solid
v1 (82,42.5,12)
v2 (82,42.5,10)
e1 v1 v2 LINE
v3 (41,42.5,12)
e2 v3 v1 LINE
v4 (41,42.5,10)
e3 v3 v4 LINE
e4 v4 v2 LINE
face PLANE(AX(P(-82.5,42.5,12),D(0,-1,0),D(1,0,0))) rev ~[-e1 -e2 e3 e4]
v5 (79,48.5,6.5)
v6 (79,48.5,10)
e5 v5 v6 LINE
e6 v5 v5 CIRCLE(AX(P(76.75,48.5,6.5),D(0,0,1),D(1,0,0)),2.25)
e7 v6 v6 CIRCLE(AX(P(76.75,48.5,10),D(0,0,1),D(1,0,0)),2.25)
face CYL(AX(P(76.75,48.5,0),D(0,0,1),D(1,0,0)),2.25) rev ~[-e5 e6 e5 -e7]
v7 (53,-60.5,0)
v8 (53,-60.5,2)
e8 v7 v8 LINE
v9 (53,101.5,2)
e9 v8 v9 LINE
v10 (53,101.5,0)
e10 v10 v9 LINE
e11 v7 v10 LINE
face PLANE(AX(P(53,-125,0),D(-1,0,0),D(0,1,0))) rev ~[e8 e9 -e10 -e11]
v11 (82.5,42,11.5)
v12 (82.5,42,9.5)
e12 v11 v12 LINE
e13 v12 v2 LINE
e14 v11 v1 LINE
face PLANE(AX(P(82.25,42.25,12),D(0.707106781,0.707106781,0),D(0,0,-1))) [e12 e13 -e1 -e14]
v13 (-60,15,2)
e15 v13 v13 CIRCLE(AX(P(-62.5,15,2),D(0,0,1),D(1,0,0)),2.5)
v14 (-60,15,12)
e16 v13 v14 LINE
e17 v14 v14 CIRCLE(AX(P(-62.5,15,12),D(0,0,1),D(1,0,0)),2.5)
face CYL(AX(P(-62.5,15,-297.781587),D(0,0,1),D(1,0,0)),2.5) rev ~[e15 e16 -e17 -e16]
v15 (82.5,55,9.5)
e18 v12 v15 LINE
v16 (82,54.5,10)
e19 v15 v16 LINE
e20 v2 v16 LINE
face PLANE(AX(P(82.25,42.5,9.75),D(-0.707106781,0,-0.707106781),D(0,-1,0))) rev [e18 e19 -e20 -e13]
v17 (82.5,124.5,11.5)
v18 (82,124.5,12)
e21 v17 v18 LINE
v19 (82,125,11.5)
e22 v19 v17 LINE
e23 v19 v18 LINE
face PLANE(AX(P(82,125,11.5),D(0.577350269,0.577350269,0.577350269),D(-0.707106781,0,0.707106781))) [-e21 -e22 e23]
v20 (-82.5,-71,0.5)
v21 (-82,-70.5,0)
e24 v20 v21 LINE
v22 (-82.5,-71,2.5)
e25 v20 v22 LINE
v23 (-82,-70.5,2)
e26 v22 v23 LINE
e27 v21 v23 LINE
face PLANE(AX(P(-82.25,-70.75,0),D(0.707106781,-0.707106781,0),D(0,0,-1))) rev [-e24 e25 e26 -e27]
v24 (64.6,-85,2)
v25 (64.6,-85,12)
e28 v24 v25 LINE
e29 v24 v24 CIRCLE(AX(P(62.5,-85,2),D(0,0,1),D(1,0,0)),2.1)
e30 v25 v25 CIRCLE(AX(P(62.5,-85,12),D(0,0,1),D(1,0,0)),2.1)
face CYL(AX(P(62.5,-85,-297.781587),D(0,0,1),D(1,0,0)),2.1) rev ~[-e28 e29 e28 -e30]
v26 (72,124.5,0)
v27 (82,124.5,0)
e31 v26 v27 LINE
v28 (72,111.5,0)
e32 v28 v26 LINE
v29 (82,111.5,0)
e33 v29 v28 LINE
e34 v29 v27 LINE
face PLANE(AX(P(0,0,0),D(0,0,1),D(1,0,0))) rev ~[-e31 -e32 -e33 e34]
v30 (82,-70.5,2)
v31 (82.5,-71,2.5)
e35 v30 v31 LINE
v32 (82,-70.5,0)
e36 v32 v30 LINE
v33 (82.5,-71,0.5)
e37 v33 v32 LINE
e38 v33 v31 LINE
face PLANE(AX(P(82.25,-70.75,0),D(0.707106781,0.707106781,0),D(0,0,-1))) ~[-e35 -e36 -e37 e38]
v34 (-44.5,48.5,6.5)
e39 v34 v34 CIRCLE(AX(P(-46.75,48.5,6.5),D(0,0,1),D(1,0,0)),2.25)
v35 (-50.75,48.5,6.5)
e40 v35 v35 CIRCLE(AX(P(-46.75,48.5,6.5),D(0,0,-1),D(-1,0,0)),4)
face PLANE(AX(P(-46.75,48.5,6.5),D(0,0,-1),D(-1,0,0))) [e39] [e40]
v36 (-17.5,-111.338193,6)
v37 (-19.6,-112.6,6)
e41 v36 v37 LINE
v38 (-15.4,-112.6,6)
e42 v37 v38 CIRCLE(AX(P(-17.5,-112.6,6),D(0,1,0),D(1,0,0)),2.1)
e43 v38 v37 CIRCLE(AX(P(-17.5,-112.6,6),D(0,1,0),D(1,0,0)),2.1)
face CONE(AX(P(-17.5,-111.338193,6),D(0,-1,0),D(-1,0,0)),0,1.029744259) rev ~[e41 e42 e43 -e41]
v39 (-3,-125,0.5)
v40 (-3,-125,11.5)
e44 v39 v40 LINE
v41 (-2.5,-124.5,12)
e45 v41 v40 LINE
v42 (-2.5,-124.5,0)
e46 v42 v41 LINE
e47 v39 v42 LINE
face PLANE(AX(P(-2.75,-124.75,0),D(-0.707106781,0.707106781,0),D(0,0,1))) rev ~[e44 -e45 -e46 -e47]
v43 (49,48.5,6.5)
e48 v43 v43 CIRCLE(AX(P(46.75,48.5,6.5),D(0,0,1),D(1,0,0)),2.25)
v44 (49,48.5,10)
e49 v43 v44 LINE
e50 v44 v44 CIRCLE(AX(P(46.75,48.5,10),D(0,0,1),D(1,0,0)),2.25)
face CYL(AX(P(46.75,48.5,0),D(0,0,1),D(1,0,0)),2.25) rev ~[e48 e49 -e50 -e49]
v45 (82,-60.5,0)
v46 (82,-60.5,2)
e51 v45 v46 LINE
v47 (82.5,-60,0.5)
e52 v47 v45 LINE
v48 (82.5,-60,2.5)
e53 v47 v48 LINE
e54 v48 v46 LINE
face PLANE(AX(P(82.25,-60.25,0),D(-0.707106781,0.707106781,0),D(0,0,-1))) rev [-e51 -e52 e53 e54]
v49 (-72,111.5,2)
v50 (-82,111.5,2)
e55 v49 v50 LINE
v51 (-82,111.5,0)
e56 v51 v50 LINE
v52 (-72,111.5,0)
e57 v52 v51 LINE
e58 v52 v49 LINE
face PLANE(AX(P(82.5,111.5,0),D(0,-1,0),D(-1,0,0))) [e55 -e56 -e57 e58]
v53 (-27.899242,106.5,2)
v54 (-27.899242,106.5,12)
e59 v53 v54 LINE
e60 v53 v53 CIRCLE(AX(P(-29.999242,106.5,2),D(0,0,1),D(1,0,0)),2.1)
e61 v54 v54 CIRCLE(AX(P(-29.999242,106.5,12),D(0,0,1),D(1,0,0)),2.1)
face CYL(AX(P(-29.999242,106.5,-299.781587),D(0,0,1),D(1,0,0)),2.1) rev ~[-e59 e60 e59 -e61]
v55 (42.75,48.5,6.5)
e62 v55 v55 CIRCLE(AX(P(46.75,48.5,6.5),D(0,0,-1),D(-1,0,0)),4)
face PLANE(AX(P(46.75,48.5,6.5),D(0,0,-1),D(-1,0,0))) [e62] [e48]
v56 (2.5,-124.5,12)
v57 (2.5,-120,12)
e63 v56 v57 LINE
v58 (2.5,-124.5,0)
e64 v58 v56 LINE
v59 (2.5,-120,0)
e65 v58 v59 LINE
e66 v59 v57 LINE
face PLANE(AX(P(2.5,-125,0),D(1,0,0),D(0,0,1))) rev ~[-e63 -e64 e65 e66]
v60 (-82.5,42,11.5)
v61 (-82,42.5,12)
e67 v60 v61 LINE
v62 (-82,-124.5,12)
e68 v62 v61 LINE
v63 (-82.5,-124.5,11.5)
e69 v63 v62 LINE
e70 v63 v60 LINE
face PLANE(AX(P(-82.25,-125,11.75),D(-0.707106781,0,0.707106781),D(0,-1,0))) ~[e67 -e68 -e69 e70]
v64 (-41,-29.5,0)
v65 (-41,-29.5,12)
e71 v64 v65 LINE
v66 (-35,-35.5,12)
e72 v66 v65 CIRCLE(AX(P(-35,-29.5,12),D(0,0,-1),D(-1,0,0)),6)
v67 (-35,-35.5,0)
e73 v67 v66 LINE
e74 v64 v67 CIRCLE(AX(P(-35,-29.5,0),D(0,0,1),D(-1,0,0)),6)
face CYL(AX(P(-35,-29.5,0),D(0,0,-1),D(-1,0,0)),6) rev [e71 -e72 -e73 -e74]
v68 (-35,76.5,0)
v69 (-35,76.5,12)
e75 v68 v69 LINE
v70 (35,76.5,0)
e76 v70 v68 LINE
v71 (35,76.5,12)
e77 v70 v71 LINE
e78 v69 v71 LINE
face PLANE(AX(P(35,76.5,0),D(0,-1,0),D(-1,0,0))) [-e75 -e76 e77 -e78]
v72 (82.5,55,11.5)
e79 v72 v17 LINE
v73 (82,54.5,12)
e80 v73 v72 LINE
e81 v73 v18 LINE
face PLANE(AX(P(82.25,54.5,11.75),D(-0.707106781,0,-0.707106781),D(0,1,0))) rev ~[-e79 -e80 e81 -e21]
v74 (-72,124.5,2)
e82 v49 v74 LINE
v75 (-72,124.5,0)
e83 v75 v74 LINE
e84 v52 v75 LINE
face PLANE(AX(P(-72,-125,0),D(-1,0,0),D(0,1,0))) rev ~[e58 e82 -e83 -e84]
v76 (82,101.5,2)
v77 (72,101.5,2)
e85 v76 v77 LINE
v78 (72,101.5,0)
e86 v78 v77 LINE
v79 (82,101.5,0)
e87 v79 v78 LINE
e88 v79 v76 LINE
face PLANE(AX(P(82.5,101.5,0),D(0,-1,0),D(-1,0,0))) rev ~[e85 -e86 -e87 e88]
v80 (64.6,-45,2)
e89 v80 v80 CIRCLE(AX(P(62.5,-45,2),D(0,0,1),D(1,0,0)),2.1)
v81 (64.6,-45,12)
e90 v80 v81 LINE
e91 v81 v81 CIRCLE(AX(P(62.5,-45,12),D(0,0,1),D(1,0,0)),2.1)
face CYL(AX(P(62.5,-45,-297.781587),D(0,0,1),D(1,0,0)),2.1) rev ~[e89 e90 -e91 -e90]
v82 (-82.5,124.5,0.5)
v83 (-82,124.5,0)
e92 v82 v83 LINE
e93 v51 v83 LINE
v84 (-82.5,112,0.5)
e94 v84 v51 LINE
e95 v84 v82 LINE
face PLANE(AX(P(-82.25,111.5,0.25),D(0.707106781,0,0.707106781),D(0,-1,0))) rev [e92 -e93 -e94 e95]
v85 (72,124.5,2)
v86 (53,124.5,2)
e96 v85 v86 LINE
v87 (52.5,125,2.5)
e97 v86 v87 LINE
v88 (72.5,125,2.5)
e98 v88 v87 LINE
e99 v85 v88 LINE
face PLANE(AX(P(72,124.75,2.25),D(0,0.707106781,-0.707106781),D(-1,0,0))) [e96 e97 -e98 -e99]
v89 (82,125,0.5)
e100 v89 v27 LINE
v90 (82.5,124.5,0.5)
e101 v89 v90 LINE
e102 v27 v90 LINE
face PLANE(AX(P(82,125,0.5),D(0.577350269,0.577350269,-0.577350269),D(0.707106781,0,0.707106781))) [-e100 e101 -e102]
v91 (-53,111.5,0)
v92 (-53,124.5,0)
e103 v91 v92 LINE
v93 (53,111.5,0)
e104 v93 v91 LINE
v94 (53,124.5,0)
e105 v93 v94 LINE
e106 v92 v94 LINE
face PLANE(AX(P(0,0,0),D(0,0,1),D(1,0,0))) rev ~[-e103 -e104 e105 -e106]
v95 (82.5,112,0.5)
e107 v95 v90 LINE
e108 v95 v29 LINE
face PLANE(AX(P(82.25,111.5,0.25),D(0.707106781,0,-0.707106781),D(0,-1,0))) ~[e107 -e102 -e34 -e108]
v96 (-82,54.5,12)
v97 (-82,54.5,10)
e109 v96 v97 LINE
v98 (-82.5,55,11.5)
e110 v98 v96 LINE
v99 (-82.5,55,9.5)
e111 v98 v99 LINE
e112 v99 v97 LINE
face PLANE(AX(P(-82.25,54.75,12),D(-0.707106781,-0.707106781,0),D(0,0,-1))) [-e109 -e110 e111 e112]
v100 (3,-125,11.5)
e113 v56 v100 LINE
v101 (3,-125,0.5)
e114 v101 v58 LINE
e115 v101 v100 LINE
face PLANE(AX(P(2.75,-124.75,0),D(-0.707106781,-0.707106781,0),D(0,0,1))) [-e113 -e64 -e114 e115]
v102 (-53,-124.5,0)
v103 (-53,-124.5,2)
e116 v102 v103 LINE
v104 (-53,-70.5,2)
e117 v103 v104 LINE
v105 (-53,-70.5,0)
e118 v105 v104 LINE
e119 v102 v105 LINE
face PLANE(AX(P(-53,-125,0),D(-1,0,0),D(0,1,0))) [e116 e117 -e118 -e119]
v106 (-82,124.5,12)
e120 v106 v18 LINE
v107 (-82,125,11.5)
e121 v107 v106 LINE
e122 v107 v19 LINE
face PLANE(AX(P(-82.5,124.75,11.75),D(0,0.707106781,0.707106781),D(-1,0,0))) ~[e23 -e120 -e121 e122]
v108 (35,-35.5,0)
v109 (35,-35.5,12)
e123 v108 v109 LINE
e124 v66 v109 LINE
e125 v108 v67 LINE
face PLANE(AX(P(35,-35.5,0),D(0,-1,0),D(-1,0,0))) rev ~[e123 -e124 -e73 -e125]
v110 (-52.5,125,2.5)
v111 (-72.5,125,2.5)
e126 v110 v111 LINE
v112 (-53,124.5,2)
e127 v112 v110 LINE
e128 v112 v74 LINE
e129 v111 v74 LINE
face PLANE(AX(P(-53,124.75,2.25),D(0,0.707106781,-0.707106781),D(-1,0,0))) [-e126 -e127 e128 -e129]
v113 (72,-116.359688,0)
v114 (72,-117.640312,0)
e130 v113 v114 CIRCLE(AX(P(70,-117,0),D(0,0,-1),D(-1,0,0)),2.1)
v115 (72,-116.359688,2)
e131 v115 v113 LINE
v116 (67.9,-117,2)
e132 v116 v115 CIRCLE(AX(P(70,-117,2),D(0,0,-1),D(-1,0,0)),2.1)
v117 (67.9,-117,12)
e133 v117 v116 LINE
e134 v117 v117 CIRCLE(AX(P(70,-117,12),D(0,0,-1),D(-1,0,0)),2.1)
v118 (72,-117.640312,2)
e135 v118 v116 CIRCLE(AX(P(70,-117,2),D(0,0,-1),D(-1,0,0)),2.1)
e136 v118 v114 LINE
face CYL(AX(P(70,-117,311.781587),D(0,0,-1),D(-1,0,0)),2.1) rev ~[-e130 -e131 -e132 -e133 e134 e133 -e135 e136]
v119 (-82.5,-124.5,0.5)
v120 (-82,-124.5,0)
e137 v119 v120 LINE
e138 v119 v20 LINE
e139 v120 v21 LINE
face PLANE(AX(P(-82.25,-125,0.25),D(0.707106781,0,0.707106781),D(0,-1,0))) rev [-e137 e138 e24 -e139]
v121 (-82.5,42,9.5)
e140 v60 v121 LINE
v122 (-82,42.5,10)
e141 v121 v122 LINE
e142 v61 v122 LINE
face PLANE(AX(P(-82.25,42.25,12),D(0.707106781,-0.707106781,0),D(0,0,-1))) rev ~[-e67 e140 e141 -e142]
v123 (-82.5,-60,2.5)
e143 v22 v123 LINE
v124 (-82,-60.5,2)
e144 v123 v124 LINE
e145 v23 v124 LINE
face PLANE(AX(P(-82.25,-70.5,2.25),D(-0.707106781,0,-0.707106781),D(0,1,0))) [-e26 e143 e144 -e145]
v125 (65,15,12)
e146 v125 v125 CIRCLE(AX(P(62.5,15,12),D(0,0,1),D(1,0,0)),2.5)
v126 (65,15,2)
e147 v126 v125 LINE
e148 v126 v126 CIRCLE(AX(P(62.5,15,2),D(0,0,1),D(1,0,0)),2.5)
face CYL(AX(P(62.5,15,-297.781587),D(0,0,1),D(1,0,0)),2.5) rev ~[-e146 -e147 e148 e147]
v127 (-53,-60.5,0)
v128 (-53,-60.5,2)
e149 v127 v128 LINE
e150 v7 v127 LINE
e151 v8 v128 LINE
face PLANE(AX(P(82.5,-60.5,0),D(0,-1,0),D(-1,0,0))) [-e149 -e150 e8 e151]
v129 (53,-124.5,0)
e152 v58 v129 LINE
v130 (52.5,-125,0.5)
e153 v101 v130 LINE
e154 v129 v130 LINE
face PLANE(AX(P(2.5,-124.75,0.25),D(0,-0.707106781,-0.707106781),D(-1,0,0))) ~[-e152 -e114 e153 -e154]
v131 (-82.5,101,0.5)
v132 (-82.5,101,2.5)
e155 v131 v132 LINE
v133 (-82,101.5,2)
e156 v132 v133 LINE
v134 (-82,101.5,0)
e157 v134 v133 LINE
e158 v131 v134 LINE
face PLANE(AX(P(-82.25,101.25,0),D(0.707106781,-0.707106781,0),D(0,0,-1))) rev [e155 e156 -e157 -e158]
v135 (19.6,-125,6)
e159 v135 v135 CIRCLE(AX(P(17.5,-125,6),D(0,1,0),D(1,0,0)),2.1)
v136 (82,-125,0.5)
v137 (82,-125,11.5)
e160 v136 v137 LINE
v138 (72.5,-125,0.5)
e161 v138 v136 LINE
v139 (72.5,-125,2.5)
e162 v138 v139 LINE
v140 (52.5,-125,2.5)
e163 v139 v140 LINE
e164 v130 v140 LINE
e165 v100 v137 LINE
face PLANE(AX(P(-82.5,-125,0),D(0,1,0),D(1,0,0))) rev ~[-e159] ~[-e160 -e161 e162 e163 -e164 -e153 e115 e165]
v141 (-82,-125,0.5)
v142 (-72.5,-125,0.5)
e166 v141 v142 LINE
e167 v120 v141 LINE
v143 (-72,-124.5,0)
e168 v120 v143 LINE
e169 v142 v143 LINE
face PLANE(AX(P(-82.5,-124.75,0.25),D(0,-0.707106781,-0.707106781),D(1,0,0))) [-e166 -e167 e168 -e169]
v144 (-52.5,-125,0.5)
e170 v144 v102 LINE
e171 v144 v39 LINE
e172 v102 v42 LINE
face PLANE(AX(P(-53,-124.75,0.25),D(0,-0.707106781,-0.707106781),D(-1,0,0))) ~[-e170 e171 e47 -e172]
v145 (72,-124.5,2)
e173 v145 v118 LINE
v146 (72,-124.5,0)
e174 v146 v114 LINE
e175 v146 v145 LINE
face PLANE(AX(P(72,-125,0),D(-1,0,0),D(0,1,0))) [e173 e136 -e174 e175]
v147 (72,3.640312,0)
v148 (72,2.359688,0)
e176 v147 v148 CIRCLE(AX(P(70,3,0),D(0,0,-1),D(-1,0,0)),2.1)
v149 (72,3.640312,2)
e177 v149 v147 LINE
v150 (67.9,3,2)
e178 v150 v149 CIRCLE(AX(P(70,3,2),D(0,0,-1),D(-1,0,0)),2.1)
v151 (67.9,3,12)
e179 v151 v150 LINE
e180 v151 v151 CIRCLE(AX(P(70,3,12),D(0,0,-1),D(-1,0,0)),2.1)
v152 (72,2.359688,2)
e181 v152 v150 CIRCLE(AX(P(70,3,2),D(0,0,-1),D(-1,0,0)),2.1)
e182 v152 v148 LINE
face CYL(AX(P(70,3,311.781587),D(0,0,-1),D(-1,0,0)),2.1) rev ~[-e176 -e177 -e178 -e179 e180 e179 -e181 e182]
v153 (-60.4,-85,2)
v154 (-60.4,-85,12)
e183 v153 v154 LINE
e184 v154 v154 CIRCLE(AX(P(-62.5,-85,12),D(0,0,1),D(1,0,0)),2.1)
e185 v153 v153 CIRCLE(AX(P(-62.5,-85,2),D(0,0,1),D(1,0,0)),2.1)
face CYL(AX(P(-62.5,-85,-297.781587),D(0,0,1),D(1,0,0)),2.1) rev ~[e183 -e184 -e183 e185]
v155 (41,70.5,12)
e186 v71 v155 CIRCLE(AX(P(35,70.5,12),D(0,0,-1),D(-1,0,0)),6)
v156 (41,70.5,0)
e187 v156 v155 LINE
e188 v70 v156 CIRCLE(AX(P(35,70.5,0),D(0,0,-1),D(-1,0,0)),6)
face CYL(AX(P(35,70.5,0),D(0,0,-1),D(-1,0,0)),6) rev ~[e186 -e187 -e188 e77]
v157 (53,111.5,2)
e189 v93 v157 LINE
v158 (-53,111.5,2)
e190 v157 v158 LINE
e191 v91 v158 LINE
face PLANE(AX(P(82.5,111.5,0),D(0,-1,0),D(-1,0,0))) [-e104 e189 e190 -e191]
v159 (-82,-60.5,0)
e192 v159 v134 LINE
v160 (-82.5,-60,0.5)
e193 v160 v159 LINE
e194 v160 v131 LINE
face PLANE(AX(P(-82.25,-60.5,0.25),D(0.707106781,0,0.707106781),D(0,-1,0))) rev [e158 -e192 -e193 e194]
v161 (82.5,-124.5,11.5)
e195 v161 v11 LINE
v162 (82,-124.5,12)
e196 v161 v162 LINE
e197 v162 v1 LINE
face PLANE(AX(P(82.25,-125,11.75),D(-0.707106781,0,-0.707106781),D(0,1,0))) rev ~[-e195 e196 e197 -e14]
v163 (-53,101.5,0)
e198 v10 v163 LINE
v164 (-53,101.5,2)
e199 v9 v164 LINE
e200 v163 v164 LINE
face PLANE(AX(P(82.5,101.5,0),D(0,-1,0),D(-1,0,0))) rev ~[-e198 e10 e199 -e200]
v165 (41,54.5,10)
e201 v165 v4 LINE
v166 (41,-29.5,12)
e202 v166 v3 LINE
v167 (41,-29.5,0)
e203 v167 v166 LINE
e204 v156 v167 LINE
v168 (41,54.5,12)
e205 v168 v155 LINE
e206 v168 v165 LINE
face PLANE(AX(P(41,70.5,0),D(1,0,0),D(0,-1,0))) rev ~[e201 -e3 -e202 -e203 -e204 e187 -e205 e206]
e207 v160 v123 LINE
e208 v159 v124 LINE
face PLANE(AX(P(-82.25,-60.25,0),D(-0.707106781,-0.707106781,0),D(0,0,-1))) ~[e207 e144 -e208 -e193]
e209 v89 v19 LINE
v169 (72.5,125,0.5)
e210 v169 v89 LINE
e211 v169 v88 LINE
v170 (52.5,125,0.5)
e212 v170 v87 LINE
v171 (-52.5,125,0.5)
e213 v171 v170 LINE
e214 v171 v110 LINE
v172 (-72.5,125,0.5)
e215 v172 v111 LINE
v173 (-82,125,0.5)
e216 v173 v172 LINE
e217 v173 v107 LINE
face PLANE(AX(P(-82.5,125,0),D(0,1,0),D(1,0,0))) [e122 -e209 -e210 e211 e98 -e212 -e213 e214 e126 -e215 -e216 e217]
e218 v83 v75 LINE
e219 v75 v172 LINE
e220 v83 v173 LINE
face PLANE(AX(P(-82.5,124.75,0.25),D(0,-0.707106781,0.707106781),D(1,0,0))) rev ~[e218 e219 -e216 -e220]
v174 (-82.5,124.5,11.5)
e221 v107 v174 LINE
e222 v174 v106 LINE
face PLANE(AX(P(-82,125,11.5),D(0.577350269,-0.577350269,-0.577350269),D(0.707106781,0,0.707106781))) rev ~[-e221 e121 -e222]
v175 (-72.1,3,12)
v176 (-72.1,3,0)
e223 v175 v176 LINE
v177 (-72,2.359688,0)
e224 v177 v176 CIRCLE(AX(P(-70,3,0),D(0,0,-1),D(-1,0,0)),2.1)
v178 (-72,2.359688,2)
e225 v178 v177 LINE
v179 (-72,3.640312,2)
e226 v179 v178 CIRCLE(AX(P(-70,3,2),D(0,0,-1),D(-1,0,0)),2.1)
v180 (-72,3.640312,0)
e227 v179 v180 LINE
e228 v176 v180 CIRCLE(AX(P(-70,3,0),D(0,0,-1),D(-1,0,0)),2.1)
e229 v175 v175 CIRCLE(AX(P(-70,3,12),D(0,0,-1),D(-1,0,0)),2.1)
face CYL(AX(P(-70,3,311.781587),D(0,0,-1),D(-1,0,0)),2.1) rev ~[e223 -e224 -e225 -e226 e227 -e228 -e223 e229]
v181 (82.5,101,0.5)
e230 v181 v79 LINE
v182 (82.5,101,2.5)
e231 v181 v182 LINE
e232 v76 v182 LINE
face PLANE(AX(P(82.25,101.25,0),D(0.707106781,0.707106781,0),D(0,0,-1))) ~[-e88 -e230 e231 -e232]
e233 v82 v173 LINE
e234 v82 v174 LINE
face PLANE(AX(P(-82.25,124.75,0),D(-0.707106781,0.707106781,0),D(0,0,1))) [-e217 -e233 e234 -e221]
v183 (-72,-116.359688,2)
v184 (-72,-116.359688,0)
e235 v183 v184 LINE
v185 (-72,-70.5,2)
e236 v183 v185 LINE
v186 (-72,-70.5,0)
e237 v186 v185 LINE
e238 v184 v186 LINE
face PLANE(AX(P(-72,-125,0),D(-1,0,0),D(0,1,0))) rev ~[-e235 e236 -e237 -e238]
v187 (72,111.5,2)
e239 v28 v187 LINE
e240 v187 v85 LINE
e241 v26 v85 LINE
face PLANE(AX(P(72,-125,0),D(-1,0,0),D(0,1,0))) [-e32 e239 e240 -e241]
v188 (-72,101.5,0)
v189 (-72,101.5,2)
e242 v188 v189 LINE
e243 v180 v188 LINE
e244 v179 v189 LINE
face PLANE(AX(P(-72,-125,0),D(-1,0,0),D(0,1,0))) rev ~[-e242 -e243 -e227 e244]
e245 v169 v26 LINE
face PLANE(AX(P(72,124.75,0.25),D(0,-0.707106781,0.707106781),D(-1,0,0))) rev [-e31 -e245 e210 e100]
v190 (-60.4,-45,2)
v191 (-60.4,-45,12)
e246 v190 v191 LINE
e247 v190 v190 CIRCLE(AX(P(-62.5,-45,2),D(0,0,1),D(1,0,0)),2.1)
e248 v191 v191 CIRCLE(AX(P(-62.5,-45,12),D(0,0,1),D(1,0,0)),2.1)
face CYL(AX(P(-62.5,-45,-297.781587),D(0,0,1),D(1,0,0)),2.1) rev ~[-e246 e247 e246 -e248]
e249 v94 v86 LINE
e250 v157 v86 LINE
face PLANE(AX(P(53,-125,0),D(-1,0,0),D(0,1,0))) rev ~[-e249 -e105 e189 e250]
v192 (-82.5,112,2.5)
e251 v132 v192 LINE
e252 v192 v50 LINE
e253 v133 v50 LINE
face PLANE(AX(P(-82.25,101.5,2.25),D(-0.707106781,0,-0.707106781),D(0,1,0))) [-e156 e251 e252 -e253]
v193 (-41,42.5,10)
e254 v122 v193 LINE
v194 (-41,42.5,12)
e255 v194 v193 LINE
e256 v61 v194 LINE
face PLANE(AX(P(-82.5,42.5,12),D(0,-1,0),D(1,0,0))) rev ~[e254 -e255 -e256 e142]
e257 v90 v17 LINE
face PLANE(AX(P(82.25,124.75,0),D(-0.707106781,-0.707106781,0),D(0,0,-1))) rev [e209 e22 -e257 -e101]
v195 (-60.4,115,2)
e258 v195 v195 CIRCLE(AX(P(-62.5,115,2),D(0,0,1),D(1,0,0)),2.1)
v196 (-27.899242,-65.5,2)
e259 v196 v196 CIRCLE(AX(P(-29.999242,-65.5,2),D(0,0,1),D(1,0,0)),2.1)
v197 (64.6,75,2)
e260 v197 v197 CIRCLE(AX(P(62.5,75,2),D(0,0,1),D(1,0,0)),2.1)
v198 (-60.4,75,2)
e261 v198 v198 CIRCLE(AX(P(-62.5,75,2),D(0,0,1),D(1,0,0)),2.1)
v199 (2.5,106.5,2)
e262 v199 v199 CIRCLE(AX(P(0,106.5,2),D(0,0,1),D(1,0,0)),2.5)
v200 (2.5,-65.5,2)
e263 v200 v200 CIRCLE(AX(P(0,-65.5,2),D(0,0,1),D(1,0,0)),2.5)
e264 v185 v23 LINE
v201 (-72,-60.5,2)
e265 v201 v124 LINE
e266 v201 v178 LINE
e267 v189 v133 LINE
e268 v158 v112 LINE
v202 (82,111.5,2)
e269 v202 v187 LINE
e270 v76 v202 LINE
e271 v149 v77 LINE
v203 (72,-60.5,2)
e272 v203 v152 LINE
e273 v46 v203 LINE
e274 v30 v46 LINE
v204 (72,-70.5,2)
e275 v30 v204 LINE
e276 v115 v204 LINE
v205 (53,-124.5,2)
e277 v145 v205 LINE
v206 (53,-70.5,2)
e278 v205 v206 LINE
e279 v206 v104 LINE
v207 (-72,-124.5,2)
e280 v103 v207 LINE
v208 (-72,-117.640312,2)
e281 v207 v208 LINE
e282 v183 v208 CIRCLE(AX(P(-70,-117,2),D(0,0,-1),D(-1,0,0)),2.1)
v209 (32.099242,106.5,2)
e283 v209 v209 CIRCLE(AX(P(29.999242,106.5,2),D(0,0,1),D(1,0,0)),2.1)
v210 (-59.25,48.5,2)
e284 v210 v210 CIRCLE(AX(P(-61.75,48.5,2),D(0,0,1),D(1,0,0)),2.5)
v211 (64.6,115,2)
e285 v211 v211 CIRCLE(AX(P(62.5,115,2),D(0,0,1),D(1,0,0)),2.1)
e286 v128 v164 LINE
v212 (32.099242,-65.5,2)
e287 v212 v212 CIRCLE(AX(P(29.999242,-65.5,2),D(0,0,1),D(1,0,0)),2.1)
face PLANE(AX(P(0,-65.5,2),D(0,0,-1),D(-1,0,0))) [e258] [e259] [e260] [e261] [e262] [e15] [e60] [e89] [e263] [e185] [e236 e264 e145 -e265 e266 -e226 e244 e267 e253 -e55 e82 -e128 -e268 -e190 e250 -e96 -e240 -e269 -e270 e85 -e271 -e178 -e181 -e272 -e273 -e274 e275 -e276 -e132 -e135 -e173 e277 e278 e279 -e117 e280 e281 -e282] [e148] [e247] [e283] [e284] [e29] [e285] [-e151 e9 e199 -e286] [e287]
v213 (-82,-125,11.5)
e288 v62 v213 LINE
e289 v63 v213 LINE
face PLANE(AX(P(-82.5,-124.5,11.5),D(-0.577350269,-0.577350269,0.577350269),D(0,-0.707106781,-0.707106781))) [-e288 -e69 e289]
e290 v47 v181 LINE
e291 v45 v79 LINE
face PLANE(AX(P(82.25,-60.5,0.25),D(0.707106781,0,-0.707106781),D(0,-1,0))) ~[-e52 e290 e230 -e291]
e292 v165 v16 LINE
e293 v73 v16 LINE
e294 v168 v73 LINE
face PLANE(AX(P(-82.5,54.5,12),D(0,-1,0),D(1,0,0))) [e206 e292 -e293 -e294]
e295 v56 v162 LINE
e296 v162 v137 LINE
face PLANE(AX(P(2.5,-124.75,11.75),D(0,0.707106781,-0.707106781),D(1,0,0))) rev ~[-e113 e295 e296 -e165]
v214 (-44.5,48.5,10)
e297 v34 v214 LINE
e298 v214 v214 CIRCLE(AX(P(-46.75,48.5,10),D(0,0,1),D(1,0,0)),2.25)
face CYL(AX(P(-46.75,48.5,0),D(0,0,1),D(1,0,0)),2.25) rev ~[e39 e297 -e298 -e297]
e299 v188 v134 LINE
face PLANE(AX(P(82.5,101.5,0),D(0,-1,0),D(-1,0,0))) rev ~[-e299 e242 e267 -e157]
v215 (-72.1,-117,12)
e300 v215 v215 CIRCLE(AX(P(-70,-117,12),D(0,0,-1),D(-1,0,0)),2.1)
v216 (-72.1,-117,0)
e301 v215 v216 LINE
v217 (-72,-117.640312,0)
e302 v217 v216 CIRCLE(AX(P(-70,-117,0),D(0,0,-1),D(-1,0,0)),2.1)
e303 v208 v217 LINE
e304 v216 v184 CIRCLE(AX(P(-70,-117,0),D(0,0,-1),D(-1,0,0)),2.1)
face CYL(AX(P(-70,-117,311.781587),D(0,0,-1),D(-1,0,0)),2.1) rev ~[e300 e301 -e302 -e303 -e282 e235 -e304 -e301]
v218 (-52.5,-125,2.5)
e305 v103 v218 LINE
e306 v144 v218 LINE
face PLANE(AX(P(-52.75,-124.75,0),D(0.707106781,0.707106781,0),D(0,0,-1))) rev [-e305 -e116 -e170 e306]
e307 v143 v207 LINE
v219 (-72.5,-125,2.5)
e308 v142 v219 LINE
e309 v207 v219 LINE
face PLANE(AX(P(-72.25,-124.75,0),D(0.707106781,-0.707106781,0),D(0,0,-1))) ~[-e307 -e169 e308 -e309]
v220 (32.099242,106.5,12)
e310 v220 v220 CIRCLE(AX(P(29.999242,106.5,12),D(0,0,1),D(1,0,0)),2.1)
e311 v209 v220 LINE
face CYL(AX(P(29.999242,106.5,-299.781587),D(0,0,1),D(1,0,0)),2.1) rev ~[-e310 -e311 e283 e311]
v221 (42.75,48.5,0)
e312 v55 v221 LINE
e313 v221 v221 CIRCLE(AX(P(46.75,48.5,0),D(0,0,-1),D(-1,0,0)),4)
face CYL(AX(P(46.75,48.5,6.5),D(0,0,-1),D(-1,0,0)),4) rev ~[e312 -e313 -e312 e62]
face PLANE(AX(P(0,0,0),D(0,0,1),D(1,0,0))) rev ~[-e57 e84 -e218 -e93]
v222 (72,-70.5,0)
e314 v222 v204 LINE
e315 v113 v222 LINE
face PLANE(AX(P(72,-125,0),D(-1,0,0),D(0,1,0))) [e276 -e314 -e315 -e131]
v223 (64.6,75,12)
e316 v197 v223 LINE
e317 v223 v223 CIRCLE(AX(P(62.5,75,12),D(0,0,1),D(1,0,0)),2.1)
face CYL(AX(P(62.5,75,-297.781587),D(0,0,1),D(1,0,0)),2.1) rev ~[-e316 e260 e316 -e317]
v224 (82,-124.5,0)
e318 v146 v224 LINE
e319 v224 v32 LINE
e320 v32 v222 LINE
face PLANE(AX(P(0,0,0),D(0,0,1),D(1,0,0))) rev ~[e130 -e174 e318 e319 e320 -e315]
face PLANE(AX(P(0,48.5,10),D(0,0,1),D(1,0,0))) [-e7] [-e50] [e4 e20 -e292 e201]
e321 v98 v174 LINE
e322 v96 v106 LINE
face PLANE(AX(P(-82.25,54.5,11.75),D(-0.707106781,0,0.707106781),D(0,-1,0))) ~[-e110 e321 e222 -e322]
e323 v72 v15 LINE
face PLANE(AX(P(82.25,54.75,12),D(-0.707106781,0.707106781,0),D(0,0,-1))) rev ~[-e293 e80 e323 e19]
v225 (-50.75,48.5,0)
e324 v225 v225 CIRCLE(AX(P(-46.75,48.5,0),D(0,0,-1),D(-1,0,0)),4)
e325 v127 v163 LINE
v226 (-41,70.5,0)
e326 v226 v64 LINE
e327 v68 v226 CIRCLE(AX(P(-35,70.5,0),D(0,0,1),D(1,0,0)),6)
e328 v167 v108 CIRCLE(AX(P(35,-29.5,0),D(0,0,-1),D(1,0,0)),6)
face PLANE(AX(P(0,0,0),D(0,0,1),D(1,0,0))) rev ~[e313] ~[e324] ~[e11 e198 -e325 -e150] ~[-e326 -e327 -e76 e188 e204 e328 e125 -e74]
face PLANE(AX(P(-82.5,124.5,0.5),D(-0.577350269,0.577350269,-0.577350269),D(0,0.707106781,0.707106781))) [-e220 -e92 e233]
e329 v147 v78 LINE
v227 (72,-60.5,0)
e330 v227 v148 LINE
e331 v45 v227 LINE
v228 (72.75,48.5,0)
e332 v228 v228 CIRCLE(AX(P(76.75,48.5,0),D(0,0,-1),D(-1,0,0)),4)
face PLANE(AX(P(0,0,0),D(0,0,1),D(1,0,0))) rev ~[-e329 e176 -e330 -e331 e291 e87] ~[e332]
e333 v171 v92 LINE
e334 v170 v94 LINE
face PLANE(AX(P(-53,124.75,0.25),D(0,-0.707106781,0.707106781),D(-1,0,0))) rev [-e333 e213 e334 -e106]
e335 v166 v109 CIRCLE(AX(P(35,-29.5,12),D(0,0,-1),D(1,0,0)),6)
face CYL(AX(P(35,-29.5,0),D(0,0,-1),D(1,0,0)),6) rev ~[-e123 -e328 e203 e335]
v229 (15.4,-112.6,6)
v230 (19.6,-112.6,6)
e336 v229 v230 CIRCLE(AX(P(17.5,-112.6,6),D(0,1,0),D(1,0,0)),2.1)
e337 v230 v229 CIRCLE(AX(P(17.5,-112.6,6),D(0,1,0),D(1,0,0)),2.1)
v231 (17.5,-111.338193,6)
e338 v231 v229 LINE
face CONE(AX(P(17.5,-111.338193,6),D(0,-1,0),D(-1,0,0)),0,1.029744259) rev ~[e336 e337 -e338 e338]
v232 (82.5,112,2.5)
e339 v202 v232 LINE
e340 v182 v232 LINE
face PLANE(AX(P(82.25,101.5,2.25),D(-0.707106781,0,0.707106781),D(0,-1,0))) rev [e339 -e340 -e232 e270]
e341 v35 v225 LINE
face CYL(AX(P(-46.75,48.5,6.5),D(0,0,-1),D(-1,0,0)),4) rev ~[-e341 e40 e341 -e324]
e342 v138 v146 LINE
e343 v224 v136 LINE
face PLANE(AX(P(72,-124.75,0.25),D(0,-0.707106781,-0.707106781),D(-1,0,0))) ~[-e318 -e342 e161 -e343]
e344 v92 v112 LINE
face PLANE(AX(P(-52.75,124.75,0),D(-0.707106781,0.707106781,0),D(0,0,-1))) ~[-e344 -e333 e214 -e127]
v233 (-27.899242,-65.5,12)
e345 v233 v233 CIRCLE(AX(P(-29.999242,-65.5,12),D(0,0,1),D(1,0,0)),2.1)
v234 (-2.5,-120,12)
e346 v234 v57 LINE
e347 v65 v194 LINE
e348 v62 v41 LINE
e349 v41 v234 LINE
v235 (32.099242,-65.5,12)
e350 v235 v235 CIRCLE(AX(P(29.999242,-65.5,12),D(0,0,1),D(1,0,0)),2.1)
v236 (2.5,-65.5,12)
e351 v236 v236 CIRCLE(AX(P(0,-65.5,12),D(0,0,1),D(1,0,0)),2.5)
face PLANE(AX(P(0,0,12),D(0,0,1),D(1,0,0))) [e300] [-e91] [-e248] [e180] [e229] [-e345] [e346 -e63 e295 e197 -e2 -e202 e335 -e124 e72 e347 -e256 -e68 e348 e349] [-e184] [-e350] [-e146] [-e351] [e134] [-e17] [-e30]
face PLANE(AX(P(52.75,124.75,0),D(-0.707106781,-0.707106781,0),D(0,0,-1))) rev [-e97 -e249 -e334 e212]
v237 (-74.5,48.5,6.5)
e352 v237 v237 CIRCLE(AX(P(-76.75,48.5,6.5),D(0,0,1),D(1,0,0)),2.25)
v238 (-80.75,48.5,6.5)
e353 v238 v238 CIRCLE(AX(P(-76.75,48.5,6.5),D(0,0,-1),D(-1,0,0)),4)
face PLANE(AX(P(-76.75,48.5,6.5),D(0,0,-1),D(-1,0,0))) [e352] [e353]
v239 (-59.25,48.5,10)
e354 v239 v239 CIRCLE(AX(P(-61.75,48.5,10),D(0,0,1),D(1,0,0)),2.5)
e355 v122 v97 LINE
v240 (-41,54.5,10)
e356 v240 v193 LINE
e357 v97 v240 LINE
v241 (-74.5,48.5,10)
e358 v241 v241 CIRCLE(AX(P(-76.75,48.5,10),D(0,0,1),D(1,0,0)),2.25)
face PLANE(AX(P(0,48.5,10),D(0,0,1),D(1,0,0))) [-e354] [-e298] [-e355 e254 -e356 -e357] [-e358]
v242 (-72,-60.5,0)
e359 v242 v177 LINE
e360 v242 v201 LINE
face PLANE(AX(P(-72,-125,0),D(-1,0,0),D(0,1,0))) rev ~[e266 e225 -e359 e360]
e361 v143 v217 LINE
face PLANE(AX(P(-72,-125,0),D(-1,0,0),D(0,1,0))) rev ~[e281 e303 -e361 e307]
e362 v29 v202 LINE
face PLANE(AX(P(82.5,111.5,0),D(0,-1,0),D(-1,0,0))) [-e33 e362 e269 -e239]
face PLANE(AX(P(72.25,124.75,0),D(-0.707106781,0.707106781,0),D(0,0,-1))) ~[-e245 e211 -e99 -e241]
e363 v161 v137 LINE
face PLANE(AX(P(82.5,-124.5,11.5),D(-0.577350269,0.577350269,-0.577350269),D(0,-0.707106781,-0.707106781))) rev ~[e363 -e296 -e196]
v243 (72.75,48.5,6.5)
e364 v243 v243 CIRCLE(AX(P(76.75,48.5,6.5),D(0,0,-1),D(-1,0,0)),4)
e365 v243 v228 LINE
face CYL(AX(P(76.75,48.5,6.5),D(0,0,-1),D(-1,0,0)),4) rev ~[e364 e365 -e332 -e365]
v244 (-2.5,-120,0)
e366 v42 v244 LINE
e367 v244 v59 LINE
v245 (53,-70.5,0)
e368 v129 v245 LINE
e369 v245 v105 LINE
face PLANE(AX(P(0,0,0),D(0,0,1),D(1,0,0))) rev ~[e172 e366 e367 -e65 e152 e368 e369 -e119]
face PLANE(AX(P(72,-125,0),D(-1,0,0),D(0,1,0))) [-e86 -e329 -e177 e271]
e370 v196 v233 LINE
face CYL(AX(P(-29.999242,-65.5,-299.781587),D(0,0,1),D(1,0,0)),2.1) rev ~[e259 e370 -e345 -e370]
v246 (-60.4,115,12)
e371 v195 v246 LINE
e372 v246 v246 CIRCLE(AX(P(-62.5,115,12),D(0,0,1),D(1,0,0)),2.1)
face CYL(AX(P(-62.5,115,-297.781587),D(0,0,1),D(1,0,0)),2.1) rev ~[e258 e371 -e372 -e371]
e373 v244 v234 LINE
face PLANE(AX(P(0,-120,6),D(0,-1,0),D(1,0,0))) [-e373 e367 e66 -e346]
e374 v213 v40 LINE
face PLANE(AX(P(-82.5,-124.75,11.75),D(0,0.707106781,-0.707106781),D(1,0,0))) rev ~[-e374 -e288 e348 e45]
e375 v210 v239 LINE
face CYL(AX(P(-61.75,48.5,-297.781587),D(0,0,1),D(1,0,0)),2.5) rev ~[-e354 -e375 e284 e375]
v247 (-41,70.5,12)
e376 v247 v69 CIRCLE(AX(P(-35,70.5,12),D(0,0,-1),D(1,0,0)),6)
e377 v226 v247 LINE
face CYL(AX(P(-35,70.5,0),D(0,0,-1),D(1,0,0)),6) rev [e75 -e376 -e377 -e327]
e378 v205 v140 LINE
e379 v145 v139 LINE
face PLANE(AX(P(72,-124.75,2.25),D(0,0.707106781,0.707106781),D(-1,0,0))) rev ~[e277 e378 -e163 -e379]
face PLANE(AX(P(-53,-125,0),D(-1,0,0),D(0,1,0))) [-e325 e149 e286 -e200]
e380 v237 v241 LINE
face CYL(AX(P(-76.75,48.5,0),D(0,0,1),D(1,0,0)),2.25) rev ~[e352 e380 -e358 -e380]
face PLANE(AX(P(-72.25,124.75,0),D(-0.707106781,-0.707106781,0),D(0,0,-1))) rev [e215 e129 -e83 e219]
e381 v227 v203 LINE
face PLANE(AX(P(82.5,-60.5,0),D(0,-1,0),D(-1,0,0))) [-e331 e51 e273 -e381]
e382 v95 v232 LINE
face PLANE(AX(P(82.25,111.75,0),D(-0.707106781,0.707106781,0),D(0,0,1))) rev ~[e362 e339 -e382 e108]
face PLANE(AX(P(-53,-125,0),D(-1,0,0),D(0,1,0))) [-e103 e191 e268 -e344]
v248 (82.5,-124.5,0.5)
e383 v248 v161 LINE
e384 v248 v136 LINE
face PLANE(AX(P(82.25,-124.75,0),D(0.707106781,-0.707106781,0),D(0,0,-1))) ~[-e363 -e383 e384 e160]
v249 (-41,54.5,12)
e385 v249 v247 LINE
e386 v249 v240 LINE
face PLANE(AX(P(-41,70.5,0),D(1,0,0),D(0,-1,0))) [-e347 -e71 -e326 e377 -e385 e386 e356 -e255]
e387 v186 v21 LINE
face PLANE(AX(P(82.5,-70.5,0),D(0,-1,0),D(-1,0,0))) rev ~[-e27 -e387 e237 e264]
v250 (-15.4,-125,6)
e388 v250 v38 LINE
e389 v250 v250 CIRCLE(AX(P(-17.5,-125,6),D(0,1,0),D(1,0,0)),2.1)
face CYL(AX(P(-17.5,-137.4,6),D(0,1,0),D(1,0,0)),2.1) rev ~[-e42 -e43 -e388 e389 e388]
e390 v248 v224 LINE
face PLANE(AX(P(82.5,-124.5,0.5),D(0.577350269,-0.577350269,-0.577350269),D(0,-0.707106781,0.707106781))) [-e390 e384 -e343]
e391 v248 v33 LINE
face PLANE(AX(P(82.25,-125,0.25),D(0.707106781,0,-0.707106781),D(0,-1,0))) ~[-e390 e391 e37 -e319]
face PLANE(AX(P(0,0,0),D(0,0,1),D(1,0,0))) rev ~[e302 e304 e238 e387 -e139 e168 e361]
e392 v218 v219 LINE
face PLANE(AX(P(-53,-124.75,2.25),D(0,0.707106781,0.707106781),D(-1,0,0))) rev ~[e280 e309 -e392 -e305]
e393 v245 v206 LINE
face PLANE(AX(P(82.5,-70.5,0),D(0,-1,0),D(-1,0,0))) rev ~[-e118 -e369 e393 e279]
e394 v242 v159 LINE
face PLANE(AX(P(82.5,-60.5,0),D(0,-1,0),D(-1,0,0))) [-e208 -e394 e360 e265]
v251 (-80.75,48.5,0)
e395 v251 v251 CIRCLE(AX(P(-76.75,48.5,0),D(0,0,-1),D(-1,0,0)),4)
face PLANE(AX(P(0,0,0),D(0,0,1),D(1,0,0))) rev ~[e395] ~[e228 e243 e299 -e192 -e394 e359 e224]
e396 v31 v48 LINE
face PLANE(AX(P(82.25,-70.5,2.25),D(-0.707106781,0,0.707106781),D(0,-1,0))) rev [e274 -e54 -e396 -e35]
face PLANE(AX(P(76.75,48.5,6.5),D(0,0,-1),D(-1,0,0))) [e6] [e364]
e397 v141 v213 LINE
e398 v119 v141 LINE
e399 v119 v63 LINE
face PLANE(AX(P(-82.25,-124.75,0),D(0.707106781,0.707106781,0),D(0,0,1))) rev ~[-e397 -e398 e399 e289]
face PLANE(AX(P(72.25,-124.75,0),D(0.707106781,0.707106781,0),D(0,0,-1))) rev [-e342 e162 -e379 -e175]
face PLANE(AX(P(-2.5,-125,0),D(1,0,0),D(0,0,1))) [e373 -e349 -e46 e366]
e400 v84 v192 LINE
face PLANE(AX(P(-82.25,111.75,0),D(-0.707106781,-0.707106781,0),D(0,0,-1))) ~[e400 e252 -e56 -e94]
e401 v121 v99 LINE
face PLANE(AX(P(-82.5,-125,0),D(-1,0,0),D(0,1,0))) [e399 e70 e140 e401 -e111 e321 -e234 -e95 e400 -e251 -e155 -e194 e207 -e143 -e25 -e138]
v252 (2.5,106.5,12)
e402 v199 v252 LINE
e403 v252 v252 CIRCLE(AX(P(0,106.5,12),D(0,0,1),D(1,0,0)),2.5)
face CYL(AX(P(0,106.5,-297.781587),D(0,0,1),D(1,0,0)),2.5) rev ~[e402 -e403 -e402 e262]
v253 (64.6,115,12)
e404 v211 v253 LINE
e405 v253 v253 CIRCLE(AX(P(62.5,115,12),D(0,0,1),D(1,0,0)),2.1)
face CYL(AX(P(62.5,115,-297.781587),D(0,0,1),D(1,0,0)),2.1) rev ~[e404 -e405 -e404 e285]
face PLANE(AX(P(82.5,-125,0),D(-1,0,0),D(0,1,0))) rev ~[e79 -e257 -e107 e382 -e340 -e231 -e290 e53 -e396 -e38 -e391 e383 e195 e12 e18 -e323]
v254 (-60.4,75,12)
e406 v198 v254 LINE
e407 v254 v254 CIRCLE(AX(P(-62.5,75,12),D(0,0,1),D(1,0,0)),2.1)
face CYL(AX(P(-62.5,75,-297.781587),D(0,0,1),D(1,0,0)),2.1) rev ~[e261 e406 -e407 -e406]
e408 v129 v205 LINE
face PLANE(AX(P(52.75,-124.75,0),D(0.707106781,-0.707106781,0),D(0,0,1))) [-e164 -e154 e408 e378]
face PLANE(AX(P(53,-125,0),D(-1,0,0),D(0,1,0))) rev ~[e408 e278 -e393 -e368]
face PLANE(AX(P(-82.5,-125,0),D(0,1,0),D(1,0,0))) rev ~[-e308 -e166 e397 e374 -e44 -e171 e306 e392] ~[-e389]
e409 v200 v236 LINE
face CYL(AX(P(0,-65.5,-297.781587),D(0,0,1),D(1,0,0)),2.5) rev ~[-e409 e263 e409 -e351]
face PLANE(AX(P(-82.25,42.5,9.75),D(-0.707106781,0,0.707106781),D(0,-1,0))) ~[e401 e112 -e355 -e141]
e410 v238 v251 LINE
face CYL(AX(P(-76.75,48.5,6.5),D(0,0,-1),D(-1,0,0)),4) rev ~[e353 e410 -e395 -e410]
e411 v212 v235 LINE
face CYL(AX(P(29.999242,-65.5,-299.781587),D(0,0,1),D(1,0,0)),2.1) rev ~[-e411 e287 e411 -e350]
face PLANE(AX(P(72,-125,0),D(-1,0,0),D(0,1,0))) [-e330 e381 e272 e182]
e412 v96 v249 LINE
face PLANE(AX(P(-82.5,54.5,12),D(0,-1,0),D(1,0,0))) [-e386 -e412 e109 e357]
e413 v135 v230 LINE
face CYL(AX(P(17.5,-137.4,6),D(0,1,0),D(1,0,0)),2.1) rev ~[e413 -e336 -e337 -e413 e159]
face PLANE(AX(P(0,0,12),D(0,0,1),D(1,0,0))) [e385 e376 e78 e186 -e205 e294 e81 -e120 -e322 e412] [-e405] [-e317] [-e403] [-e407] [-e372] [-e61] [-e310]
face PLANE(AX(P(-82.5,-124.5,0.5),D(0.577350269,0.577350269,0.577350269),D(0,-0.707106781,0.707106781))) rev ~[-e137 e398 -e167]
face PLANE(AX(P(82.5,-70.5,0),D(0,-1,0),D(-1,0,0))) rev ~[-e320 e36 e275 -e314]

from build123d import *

# Parameters (mm, degrees)
SKETCH_1_W                   = 165
SKETCH_1_H                   = 250
EXTRUDE_1_DEPTH              = 12
SKETCH_2_W                   = 19
SKETCH_2_H                   = 250
CUT_EXTRUDE_1_DEPTH          = 2
SKETCH_3_W                   = 165
SKETCH_3_H                   = 10
CUT_EXTRUDE_2_DEPTH          = 2
SKETCH_4_W                   = 165
SKETCH_4_H                   = 10
CUT_EXTRUDE_3_DEPTH          = 2
HOLE_WIZARD_M5_1_D           = 4.2
MM_1_D                       = 5
CUT_EXTRUDE_4_DEPTH          = 151.250623959
SKETCH_11_W                  = 70
SKETCH_11_H                  = 112
CUT_EXTRUDE_5_DEPTH          = 151.250623959
SKETCH_13_W                  = 165
SKETCH_13_H                  = 12
CUT_EXTRUDE_6_DEPTH          = 2
HOLE_WIZARD_M5_2_D           = 4.2
HOLE_WIZARD_M4_1_D           = 4.5
HOLE_WIZARD_M4_1_CBORE_D     = 8
HOLE_WIZARD_M4_1_CBORE_DEPTH = 6.5
MM_2_D                       = 5
HOLE_WIZARD_M5_3_D           = 4.2
HOLE_WIZARD_M5_3_DEPTH       = 12.4
HOLE_WIZARD_M5_3_TIP         = 1.2618073
SKETCH_22_W                  = 5
SKETCH_22_H                  = 12
CUT_EXTRUDE_7_DEPTH          = 5
HOLE_WIZARD_M5_4_D           = 4.2
MM_3_D                       = 5
CHAMFER_1_SIZE               = 0.5


with BuildPart() as part:
    # 草图1 → 凸台-拉伸1 (new body)
    with BuildSketch(Plane.XY):
        Rectangle(SKETCH_1_W, SKETCH_1_H)
    extrude(amount=EXTRUDE_1_DEPTH)

    # 草图2 → 切除-拉伸1 (cut)
    with BuildSketch(Plane(origin=(0, 0, 0), x_dir=(-1, 0, 0), z_dir=(0, 0, -1))):
        with Locations((62.5, 0)):
            Rectangle(SKETCH_2_W, SKETCH_2_H)
        with Locations((-62.5, 0)):
            Rectangle(SKETCH_2_W, SKETCH_2_H)
    extrude(amount=-CUT_EXTRUDE_1_DEPTH, mode=Mode.SUBTRACT)

    # 草图3 → 切除-拉伸2 (cut)
    with BuildSketch(Plane(origin=(0, 0, 0), x_dir=(-1, 0, 0), z_dir=(0, 0, -1))):
        with Locations((0, -65.5)):
            Rectangle(SKETCH_3_W, SKETCH_3_H)
    extrude(amount=-CUT_EXTRUDE_2_DEPTH, mode=Mode.SUBTRACT)

    # 草图4 → 切除-拉伸3 (cut)
    with BuildSketch(Plane(origin=(0, 0, 0), x_dir=(-1, 0, 0), z_dir=(0, 0, -1))):
        with Locations((0, 106.5)):
            Rectangle(SKETCH_4_W, SKETCH_4_H)
    extrude(amount=-CUT_EXTRUDE_3_DEPTH, mode=Mode.SUBTRACT)

    # M5 螺纹孔1 (through all)
    with Locations(Plane(origin=(0, 0, 0), x_dir=(-1, 0, 0), z_dir=(0, 0, -1))):
        with Locations((-29.999242405, -65.5), (29.999242405, -65.5), (29.999242405, 106.5), (-29.999242405, 106.5)):
            Hole(HOLE_WIZARD_M5_1_D / 2)

    # 大小mm 暗销孔1 (through all)
    with Locations(Plane(origin=(0, 0, 2), x_dir=(-1, 0, 0), z_dir=(0, 0, -1))):
        with Locations((0, -65.5), (0, 106.5)):
            Hole(MM_1_D / 2)

    # 草图10 → 切除-拉伸4 (cut, through all)
    with BuildSketch(Plane(origin=(0, 0, 0), x_dir=(-1, 0, 0), z_dir=(0, 0, -1))):
        with BuildLine():
            Line((29, -29.5), (29, 70.5))
            ThreePointArc((29, 70.5), (35, 76.5), (41, 70.5))
            Line((41, 70.5), (41, -29.5))
            ThreePointArc((41, -29.5), (35, -35.5), (29, -29.5))
        make_face()
        with BuildLine():
            Line((-29, -29.5), (-29, 70.5))
            ThreePointArc((-29, 70.5), (-35, 76.5), (-41, 70.5))
            Line((-41, 70.5), (-41, -29.5))
            ThreePointArc((-41, -29.5), (-35, -35.5), (-29, -29.5))
        make_face()
    extrude(amount=-CUT_EXTRUDE_4_DEPTH, mode=Mode.SUBTRACT)

    # 草图11 → 切除-拉伸5 (cut, through all)
    with BuildSketch(Plane(origin=(0, 0, 0), x_dir=(-1, 0, 0), z_dir=(0, 0, -1))):
        with Locations((0, 20.5)):
            Rectangle(SKETCH_11_W, SKETCH_11_H)
    extrude(amount=-CUT_EXTRUDE_5_DEPTH, mode=Mode.SUBTRACT)

    # 草图13 → 切除-拉伸6 (cut)
    with BuildSketch(Plane.XY.offset(12)):
        with Locations((0, 48.5)):
            Rectangle(SKETCH_13_W, SKETCH_13_H)
    extrude(amount=-CUT_EXTRUDE_6_DEPTH, mode=Mode.SUBTRACT)

    # M5 螺纹孔2 (through all)
    with Locations(Plane.XY.offset(12)):
        with Locations((-70, 3), (-70, -117), (70, 3), (70, -117)):
            Hole(HOLE_WIZARD_M5_2_D / 2)

    # M4 六角凹头螺钉的柱形沉头孔1 (through all)
    with Locations(Plane(origin=(0, 0, 0), x_dir=(-1, 0, 0), z_dir=(0, 0, -1))):
        with Locations((46.75, 48.5), (76.75, 48.5), (-76.75, 48.5), (-46.75, 48.5)):
            CounterBoreHole(HOLE_WIZARD_M4_1_D / 2, HOLE_WIZARD_M4_1_CBORE_D / 2, HOLE_WIZARD_M4_1_CBORE_DEPTH)

    # 大小mm 暗销孔2 (through all)
    with Locations(Plane(origin=(0, 0, 2), x_dir=(-1, 0, 0), z_dir=(0, 0, -1))):
        with Locations((61.75, 48.5)):
            Hole(MM_2_D / 2)

    # M5 螺纹孔3
    with Locations(Plane(origin=(0, -125, 0), x_dir=(-1, 0, 0), z_dir=(0, -1, 0))):
        with Locations((-17.5, -6), (17.5, -6)):
            Hole(HOLE_WIZARD_M5_3_D / 2, depth=HOLE_WIZARD_M5_3_DEPTH)
            with Locations((0, 0, -(HOLE_WIZARD_M5_3_DEPTH + HOLE_WIZARD_M5_3_TIP / 2))):  # 118° drill point
                Cone(0, HOLE_WIZARD_M5_3_D / 2, HOLE_WIZARD_M5_3_TIP, mode=Mode.SUBTRACT)

    # 草图22 → 切除-拉伸7 (cut)
    with BuildSketch(Plane.XZ.offset(125)):
        with Locations((0, 6)):
            Rectangle(SKETCH_22_W, SKETCH_22_H)
    extrude(amount=-CUT_EXTRUDE_7_DEPTH, mode=Mode.SUBTRACT)

    # M5 螺纹孔4 (through all)
    with Locations(Plane(origin=(0, 0, 2), x_dir=(-1, 0, 0), z_dir=(0, 0, -1))):
        with Locations((62.5, -85), (62.5, -45), (62.5, 75), (62.5, 115), (-62.5, 115), (-62.5, 75), (-62.5, -45), (-62.5, -85)):
            Hole(HOLE_WIZARD_M5_4_D / 2)

    # 大小mm 暗销孔3 (through all)
    with Locations(Plane(origin=(0, 0, 2), x_dir=(-1, 0, 0), z_dir=(0, 0, -1))):
        with Locations((62.5, 15), (-62.5, 15)):
            Hole(MM_3_D / 2)

    # 倒角1
    chamfer_1_edges = [part.edges().sort_by_distance(p)[0] for p in [
        (82.5, 118.25, 0),
        (-82.5, 20.5, 0),
        (82.5, 111.5, 1),
        (-82.5, 101.5, 1),
        (82.5, 106.5, 2),
        (82.5, 101.5, 1),
        (-82.5, 106.5, 2),
        (-82.5, 111.5, 1),
        (-82.5, 89.75, 12),
        (-27.75, -125, 0),
        (77.25, -125, 0),
        (0, 125, 0),
        (-77.25, 125, 0),
        (-42.5, -125, 12),
        (-72, 125, 1),
        (-62.5, -125, 2),
        (-72, -125, 1),
        (-53, -125, 1),
        (-62.5, 125, 2),
        (-53, 125, 1),
        (82.5, 89.75, 12),
        (-82.5, -41.25, 12),
        (-82.5, 54.5, 11),
        (82.5, 42.5, 11),
        (-82.5, 48.5, 10),
        (-82.5, 42.5, 11),
        (82.5, 48.5, 10),
        (82.5, 54.5, 11),
        (62.5, 125, 2),
        (72, 125, 1),
        (53, 125, 1),
        (62.5, -125, 2),
        (53, -125, 1),
        (72, -125, 1),
        (27.75, -125, 0),
        (42.5, -125, 12),
        (-2.5, -125, 6),
        (2.5, -125, 6),
        (82.5, -41.25, 12),
        (-77.25, -125, 0),
        (-82.5, 118.25, 0),
        (82.5, 20.5, 0),
        (-82.5, -97.75, 0),
        (77.25, 125, 0),
        (82.5, -97.75, 0),
        (-82.5, -70.5, 1),
        (82.5, -60.5, 1),
        (-82.5, -65.5, 2),
        (-82.5, -60.5, 1),
        (82.5, -65.5, 2),
        (82.5, -70.5, 1),
        (82.5, -125, 6),
        (-82.5, -125, 6),
        (-82.5, 125, 6),
        (82.5, 125, 6),
        (0, 125, 12),
    ]]
    chamfer(chamfer_1_edges, length=CHAMFER_1_SIZE)


solid = part.part
